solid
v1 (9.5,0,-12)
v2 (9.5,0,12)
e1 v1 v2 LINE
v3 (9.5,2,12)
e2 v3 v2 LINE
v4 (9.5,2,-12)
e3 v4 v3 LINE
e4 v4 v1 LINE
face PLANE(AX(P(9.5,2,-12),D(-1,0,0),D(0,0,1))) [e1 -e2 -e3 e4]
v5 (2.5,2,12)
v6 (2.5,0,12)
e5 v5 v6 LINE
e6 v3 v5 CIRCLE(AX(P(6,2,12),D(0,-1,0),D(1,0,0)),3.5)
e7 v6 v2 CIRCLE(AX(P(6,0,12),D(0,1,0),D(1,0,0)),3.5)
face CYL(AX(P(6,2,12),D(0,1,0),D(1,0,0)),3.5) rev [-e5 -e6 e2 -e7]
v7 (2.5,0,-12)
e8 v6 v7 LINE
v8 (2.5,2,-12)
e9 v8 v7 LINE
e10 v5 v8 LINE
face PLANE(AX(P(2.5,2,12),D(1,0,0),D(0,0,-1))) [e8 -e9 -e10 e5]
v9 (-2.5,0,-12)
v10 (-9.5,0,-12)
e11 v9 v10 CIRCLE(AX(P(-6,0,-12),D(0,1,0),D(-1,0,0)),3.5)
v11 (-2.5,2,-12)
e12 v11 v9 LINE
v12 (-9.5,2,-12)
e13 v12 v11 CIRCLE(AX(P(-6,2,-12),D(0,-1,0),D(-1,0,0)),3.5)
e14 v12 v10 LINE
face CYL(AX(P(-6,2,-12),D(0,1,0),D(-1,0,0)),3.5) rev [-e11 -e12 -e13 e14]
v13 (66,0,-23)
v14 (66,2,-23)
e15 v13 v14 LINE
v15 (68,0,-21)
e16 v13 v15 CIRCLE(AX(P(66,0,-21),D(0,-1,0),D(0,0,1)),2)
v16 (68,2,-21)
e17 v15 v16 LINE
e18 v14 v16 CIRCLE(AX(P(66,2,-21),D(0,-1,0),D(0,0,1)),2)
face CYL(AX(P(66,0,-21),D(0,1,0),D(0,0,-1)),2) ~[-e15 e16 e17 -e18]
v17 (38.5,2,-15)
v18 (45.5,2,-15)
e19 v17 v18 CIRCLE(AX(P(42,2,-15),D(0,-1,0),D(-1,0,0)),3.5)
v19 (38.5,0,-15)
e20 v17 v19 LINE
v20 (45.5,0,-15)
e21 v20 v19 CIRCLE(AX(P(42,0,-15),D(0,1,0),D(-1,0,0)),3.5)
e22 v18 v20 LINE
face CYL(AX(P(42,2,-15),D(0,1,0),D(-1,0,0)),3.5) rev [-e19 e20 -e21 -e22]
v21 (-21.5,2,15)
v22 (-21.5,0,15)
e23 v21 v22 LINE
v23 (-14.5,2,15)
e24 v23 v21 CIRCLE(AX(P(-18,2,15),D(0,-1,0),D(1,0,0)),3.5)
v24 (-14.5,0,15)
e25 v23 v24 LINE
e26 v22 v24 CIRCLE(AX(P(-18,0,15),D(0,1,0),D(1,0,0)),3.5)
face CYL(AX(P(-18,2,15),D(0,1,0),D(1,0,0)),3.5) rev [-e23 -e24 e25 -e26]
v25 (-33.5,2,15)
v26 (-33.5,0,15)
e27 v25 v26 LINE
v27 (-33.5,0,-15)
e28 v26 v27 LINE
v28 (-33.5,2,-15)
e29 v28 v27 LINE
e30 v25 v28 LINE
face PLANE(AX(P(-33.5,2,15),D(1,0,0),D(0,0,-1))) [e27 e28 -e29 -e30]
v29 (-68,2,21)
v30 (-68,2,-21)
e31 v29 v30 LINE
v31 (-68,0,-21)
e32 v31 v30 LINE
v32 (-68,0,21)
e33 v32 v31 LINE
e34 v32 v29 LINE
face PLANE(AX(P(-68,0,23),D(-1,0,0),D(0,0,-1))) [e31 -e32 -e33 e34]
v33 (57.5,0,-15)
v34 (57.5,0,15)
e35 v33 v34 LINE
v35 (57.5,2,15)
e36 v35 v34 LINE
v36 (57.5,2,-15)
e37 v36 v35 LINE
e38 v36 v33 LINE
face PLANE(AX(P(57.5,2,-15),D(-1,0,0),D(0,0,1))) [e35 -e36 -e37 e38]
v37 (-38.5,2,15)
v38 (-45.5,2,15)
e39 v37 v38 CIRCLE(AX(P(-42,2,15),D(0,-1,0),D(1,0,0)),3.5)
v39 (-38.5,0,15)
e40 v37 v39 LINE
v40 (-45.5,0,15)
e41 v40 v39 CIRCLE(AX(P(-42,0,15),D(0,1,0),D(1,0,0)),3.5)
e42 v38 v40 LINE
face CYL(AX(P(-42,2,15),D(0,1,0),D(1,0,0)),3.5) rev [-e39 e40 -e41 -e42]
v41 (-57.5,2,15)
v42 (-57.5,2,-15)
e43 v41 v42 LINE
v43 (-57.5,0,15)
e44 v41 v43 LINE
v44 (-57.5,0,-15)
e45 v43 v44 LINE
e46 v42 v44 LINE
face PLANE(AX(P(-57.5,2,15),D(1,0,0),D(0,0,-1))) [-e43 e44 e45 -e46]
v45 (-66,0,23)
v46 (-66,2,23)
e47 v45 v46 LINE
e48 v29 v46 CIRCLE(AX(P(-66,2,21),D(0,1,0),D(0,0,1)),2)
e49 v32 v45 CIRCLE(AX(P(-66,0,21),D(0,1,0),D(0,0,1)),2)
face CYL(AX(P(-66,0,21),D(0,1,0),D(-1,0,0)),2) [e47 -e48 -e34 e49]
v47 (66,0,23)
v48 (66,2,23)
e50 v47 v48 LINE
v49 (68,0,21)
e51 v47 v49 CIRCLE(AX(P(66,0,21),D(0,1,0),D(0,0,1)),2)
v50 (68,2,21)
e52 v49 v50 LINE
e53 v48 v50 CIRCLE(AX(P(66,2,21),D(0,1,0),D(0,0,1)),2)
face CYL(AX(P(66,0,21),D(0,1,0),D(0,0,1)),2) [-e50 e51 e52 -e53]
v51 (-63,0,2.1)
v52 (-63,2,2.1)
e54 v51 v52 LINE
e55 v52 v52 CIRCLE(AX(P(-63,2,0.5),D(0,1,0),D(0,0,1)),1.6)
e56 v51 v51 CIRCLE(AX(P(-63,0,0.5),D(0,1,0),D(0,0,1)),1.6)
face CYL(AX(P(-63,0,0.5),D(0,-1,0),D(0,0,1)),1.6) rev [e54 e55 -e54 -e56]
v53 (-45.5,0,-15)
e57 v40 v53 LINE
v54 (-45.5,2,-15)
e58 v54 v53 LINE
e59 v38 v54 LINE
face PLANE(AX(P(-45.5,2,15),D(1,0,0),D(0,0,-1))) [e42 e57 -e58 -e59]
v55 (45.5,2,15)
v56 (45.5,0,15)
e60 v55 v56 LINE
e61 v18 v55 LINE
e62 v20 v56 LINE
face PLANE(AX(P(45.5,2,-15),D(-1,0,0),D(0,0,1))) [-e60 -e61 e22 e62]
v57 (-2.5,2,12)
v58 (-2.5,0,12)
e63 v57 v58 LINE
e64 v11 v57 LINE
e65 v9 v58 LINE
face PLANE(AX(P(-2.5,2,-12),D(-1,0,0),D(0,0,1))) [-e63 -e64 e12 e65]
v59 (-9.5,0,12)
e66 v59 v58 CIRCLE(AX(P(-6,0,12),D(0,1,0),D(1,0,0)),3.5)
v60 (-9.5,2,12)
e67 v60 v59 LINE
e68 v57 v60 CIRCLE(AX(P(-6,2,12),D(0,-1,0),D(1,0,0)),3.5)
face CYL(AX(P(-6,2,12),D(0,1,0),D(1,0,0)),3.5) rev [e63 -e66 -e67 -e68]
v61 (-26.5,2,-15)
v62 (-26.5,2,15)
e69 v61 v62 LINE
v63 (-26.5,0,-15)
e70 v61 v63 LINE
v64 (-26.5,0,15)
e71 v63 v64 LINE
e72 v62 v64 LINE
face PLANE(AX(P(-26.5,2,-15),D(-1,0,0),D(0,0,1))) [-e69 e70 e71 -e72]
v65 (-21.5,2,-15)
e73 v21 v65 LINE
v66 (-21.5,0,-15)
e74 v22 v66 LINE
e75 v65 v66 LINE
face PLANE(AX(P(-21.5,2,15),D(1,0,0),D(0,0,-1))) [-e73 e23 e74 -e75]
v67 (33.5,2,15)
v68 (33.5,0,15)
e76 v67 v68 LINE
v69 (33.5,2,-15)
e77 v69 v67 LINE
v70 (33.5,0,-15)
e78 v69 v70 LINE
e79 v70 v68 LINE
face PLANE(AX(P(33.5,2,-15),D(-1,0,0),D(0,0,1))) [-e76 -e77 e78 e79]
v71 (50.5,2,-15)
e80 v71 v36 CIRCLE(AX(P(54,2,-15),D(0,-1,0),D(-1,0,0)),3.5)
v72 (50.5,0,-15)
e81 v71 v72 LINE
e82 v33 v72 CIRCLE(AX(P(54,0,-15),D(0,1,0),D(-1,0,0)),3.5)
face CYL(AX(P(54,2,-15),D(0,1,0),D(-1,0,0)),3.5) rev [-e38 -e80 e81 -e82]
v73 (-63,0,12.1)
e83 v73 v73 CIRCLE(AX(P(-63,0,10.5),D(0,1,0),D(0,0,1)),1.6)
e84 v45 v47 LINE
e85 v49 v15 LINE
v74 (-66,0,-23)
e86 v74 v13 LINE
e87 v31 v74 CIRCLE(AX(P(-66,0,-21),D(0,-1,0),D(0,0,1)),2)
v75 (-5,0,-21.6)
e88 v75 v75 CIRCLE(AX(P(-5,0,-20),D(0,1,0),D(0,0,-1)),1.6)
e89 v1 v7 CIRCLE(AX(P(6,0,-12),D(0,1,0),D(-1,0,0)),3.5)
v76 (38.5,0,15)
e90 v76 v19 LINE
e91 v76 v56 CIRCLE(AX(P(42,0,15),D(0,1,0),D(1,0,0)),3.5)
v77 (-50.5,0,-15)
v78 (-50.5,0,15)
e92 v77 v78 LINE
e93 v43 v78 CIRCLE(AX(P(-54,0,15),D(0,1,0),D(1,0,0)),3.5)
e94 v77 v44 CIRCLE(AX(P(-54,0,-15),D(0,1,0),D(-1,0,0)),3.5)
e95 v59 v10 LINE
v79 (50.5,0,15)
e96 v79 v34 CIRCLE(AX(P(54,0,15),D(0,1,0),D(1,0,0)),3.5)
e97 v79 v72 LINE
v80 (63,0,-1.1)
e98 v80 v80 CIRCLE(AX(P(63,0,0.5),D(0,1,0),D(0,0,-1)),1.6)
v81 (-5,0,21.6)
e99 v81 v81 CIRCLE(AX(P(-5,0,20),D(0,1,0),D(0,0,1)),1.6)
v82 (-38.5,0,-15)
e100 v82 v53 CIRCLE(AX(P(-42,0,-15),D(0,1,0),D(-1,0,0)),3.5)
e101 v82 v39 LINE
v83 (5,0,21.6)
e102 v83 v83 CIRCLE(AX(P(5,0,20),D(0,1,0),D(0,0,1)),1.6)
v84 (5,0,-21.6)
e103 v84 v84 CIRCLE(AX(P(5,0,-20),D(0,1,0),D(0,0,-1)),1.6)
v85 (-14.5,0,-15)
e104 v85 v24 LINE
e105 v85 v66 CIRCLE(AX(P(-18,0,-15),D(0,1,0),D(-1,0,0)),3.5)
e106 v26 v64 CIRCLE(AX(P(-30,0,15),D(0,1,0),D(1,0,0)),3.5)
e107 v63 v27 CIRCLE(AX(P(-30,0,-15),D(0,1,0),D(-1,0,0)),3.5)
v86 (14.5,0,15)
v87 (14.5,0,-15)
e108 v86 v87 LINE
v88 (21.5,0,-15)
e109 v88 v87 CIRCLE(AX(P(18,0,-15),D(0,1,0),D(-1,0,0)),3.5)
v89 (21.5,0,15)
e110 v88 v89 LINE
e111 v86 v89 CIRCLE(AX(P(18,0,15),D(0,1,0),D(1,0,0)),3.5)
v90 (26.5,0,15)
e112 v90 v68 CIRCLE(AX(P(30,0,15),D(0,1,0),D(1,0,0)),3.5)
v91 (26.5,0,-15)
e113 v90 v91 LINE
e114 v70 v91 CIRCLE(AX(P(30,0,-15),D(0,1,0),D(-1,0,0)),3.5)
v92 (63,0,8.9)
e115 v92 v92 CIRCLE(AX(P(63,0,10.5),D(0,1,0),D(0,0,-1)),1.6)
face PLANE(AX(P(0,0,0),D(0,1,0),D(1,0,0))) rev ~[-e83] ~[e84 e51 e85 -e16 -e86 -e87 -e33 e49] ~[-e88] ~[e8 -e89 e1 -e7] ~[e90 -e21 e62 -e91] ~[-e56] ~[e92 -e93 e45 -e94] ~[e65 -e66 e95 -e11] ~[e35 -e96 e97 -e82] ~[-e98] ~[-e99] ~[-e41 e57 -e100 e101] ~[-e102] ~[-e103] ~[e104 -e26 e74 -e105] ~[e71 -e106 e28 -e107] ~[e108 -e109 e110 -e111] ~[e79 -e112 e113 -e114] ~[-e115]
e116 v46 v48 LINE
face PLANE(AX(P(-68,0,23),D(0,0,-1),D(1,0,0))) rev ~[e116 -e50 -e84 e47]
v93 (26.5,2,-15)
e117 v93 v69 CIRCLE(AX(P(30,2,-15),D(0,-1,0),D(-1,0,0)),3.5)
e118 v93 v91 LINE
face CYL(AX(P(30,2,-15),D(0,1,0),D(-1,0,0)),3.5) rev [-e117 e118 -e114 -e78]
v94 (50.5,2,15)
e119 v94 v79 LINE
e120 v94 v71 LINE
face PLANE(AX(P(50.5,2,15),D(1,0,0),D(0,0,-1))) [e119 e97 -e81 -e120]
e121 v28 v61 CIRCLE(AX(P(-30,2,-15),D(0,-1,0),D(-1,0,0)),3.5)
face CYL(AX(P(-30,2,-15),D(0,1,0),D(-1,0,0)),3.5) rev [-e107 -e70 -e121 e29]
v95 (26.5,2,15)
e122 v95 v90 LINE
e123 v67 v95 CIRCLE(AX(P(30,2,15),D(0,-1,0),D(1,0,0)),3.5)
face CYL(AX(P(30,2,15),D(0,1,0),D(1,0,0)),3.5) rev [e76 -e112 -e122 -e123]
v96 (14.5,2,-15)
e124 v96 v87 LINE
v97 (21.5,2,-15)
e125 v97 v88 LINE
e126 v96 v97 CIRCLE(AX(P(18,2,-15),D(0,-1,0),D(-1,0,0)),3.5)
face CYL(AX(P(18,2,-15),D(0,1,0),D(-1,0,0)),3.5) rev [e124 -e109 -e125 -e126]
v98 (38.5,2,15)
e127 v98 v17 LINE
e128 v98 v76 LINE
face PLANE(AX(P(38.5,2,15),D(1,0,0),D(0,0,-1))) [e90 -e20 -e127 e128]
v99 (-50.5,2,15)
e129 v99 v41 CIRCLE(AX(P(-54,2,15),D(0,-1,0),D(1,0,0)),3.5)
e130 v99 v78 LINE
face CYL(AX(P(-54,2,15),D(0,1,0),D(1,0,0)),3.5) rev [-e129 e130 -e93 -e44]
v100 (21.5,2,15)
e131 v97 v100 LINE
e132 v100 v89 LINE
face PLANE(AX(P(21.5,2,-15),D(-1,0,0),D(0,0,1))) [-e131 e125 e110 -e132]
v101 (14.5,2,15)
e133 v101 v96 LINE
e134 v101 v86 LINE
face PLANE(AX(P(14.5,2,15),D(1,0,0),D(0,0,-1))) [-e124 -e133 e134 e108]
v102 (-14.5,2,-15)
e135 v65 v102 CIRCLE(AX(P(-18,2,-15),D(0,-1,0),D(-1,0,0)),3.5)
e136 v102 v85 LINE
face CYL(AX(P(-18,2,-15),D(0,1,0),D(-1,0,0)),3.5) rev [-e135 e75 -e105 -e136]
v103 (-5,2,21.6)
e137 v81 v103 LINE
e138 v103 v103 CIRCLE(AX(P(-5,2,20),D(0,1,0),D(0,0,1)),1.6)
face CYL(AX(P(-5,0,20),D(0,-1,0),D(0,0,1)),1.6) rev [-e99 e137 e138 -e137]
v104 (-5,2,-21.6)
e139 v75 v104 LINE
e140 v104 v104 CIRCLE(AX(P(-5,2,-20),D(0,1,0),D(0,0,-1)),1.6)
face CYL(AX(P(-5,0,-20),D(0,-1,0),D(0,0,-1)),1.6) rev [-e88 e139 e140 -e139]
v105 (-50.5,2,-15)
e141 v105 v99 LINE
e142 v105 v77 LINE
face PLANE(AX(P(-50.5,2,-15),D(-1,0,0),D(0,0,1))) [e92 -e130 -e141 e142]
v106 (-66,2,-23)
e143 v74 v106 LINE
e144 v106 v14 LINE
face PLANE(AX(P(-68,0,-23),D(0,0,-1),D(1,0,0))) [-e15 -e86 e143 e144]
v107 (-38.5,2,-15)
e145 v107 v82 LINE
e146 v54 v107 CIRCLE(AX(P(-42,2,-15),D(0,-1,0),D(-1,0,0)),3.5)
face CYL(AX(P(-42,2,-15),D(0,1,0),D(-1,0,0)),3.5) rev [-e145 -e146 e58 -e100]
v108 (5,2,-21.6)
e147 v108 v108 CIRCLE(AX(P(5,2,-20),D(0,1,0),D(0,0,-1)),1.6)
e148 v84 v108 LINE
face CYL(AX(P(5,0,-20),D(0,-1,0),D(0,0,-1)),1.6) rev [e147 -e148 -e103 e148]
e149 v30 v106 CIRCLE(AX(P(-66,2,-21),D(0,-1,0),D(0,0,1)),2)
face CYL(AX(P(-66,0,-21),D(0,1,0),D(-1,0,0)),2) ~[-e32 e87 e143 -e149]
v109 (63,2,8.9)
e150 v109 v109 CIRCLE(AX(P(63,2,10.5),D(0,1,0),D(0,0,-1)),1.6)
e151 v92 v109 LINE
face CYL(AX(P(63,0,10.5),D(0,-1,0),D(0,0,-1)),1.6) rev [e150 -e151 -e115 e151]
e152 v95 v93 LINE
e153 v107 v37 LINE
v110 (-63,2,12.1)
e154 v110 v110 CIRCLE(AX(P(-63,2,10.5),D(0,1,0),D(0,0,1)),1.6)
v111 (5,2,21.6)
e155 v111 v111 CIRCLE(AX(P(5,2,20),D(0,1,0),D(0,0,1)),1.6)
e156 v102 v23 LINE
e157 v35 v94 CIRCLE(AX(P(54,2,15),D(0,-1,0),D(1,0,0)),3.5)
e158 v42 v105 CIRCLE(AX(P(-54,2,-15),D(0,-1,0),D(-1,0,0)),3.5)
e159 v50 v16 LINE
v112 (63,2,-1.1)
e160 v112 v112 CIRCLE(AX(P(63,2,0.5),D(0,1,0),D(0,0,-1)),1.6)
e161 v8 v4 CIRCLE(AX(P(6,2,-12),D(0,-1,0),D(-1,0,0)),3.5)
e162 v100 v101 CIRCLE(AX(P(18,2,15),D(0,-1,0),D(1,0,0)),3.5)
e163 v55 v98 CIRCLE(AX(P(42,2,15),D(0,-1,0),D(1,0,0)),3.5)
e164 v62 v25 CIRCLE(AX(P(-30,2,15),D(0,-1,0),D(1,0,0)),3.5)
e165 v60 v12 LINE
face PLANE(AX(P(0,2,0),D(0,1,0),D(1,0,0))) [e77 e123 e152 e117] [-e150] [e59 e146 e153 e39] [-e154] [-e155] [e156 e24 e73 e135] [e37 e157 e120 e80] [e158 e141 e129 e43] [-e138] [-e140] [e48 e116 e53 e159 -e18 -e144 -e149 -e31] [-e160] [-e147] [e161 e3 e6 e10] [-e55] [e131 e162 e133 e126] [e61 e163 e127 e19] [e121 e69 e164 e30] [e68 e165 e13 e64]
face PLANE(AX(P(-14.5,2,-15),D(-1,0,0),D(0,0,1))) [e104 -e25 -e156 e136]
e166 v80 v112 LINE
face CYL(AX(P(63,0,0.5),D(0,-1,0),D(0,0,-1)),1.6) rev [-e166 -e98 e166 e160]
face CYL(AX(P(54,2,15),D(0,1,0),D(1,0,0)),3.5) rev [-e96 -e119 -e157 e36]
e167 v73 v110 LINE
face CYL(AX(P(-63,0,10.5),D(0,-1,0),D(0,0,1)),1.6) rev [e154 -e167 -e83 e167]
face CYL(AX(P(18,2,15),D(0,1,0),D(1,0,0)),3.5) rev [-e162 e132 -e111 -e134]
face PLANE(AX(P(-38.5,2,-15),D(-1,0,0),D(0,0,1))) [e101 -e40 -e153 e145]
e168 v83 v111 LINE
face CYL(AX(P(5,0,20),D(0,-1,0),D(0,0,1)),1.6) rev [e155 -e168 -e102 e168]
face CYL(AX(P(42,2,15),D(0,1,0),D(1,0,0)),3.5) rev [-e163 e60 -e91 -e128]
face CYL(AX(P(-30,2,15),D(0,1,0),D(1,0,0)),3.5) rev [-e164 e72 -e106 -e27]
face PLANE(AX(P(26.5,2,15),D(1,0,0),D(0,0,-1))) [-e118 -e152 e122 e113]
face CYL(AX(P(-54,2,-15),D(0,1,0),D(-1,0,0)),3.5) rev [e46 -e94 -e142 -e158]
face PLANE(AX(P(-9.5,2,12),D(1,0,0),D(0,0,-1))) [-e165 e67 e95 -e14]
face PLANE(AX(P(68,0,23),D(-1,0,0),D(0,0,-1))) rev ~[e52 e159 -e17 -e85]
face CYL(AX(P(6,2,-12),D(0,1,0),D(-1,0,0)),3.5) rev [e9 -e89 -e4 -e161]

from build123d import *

# Parameters (mm, degrees)
SKETCH_1_W          = 136
SKETCH_1_H          = 46
SKETCH_1_R          = 1.6
EXTRUDE_1_DEPTH     = 2
CUT_EXTRUDE_1_DEPTH = 72.812255222
FILLET_R2_1_R       = 2


with BuildPart() as part:
    # 草图1 → 凸台-拉伸1 (new body)
    with BuildSketch(Plane(origin=(0, 0, 0), x_dir=(1, 0, 0), z_dir=(0, 1, 0))):
        Rectangle(SKETCH_1_W, SKETCH_1_H)
        with Locations(Location((-63, -0.5, 0), (0, 0, 270))):
            Circle(SKETCH_1_R, mode=Mode.SUBTRACT)
        with Locations(Location((-63, -10.5, 0), (0, 0, 270))):
            Circle(SKETCH_1_R, mode=Mode.SUBTRACT)
        with Locations(Location((-5, -20, 0), (0, 0, 270))):
            Circle(SKETCH_1_R, mode=Mode.SUBTRACT)
        with Locations(Location((5, -20, 0), (0, 0, 270))):
            Circle(SKETCH_1_R, mode=Mode.SUBTRACT)
        with Locations(Location((63, -10.5, 0), (0, 0, 90))):
            Circle(SKETCH_1_R, mode=Mode.SUBTRACT)
        with Locations(Location((63, -0.5, 0), (0, 0, 90))):
            Circle(SKETCH_1_R, mode=Mode.SUBTRACT)
        with Locations(Location((5, 20, 0), (0, 0, 90))):
            Circle(SKETCH_1_R, mode=Mode.SUBTRACT)
        with Locations(Location((-5, 20, 0), (0, 0, 90))):
            Circle(SKETCH_1_R, mode=Mode.SUBTRACT)
    extrude(amount=EXTRUDE_1_DEPTH)

    # 草图2 → 切除-拉伸1 (cut, through all)
    with BuildSketch(Plane(origin=(0, 2, 0), x_dir=(1, 0, 0), z_dir=(0, 1, 0))):
        with BuildLine():
            Line((-50.5, 15), (-50.5, -15))
            ThreePointArc((-50.5, -15), (-54, -18.5), (-57.5, -15))
            Line((-57.5, -15), (-57.5, 15))
            ThreePointArc((-57.5, 15), (-54, 18.5), (-50.5, 15))
        make_face()
        with BuildLine():
            Line((-38.5, 15), (-38.5, -15))
            ThreePointArc((-38.5, -15), (-42, -18.5), (-45.5, -15))
            Line((-45.5, -15), (-45.5, 15))
            ThreePointArc((-45.5, 15), (-42, 18.5), (-38.5, 15))
        make_face()
        with BuildLine():
            Line((-26.5, 15), (-26.5, -15))
            ThreePointArc((-26.5, -15), (-30, -18.5), (-33.5, -15))
            Line((-33.5, -15), (-33.5, 15))
            ThreePointArc((-33.5, 15), (-30, 18.5), (-26.5, 15))
        make_face()
        with BuildLine():
            Line((-14.5, 15), (-14.5, -15))
            ThreePointArc((-14.5, -15), (-18, -18.5), (-21.5, -15))
            Line((-21.5, -15), (-21.5, 15))
            ThreePointArc((-21.5, 15), (-18, 18.5), (-14.5, 15))
        make_face()
        with BuildLine():
            Line((-2.5, 12), (-2.5, -12))
            ThreePointArc((-2.5, -12), (-6, -15.5), (-9.5, -12))
            Line((-9.5, -12), (-9.5, 12))
            ThreePointArc((-9.5, 12), (-6, 15.5), (-2.5, 12))
        make_face()
        with BuildLine():
            Line((9.5, 12), (9.5, -12))
            ThreePointArc((9.5, -12), (6, -15.5), (2.5, -12))
            Line((2.5, -12), (2.5, 12))
            ThreePointArc((2.5, 12), (6, 15.5), (9.5, 12))
        make_face()
        with BuildLine():
            Line((21.5, 15), (21.5, -15))
            ThreePointArc((21.5, -15), (18, -18.5), (14.5, -15))
            Line((14.5, -15), (14.5, 15))
            ThreePointArc((14.5, 15), (18, 18.5), (21.5, 15))
        make_face()
        with BuildLine():
            Line((33.5, 15), (33.5, -15))
            ThreePointArc((33.5, -15), (30, -18.5), (26.5, -15))
            Line((26.5, -15), (26.5, 15))
            ThreePointArc((26.5, 15), (30, 18.5), (33.5, 15))
        make_face()
        with BuildLine():
            Line((45.5, 15), (45.5, -15))
            ThreePointArc((45.5, -15), (42, -18.5), (38.5, -15))
            Line((38.5, -15), (38.5, 15))
            ThreePointArc((38.5, 15), (42, 18.5), (45.5, 15))
        make_face()
        with BuildLine():
            Line((57.5, 15), (57.5, -15))
            ThreePointArc((57.5, -15), (54, -18.5), (50.5, -15))
            Line((50.5, -15), (50.5, 15))
            ThreePointArc((50.5, 15), (54, 18.5), (57.5, 15))
        make_face()
    extrude(amount=-CUT_EXTRUDE_1_DEPTH, mode=Mode.SUBTRACT)

    # R2 圆角1
    fillet_r2_1_edges = [part.edges().sort_by_distance(p)[0] for p in [
        (-68, 1, -23),
        (68, 1, -23),
        (68, 1, 23),
        (-68, 1, 23),
    ]]
    fillet(fillet_r2_1_edges, radius=FILLET_R2_1_R)


solid = part.part
